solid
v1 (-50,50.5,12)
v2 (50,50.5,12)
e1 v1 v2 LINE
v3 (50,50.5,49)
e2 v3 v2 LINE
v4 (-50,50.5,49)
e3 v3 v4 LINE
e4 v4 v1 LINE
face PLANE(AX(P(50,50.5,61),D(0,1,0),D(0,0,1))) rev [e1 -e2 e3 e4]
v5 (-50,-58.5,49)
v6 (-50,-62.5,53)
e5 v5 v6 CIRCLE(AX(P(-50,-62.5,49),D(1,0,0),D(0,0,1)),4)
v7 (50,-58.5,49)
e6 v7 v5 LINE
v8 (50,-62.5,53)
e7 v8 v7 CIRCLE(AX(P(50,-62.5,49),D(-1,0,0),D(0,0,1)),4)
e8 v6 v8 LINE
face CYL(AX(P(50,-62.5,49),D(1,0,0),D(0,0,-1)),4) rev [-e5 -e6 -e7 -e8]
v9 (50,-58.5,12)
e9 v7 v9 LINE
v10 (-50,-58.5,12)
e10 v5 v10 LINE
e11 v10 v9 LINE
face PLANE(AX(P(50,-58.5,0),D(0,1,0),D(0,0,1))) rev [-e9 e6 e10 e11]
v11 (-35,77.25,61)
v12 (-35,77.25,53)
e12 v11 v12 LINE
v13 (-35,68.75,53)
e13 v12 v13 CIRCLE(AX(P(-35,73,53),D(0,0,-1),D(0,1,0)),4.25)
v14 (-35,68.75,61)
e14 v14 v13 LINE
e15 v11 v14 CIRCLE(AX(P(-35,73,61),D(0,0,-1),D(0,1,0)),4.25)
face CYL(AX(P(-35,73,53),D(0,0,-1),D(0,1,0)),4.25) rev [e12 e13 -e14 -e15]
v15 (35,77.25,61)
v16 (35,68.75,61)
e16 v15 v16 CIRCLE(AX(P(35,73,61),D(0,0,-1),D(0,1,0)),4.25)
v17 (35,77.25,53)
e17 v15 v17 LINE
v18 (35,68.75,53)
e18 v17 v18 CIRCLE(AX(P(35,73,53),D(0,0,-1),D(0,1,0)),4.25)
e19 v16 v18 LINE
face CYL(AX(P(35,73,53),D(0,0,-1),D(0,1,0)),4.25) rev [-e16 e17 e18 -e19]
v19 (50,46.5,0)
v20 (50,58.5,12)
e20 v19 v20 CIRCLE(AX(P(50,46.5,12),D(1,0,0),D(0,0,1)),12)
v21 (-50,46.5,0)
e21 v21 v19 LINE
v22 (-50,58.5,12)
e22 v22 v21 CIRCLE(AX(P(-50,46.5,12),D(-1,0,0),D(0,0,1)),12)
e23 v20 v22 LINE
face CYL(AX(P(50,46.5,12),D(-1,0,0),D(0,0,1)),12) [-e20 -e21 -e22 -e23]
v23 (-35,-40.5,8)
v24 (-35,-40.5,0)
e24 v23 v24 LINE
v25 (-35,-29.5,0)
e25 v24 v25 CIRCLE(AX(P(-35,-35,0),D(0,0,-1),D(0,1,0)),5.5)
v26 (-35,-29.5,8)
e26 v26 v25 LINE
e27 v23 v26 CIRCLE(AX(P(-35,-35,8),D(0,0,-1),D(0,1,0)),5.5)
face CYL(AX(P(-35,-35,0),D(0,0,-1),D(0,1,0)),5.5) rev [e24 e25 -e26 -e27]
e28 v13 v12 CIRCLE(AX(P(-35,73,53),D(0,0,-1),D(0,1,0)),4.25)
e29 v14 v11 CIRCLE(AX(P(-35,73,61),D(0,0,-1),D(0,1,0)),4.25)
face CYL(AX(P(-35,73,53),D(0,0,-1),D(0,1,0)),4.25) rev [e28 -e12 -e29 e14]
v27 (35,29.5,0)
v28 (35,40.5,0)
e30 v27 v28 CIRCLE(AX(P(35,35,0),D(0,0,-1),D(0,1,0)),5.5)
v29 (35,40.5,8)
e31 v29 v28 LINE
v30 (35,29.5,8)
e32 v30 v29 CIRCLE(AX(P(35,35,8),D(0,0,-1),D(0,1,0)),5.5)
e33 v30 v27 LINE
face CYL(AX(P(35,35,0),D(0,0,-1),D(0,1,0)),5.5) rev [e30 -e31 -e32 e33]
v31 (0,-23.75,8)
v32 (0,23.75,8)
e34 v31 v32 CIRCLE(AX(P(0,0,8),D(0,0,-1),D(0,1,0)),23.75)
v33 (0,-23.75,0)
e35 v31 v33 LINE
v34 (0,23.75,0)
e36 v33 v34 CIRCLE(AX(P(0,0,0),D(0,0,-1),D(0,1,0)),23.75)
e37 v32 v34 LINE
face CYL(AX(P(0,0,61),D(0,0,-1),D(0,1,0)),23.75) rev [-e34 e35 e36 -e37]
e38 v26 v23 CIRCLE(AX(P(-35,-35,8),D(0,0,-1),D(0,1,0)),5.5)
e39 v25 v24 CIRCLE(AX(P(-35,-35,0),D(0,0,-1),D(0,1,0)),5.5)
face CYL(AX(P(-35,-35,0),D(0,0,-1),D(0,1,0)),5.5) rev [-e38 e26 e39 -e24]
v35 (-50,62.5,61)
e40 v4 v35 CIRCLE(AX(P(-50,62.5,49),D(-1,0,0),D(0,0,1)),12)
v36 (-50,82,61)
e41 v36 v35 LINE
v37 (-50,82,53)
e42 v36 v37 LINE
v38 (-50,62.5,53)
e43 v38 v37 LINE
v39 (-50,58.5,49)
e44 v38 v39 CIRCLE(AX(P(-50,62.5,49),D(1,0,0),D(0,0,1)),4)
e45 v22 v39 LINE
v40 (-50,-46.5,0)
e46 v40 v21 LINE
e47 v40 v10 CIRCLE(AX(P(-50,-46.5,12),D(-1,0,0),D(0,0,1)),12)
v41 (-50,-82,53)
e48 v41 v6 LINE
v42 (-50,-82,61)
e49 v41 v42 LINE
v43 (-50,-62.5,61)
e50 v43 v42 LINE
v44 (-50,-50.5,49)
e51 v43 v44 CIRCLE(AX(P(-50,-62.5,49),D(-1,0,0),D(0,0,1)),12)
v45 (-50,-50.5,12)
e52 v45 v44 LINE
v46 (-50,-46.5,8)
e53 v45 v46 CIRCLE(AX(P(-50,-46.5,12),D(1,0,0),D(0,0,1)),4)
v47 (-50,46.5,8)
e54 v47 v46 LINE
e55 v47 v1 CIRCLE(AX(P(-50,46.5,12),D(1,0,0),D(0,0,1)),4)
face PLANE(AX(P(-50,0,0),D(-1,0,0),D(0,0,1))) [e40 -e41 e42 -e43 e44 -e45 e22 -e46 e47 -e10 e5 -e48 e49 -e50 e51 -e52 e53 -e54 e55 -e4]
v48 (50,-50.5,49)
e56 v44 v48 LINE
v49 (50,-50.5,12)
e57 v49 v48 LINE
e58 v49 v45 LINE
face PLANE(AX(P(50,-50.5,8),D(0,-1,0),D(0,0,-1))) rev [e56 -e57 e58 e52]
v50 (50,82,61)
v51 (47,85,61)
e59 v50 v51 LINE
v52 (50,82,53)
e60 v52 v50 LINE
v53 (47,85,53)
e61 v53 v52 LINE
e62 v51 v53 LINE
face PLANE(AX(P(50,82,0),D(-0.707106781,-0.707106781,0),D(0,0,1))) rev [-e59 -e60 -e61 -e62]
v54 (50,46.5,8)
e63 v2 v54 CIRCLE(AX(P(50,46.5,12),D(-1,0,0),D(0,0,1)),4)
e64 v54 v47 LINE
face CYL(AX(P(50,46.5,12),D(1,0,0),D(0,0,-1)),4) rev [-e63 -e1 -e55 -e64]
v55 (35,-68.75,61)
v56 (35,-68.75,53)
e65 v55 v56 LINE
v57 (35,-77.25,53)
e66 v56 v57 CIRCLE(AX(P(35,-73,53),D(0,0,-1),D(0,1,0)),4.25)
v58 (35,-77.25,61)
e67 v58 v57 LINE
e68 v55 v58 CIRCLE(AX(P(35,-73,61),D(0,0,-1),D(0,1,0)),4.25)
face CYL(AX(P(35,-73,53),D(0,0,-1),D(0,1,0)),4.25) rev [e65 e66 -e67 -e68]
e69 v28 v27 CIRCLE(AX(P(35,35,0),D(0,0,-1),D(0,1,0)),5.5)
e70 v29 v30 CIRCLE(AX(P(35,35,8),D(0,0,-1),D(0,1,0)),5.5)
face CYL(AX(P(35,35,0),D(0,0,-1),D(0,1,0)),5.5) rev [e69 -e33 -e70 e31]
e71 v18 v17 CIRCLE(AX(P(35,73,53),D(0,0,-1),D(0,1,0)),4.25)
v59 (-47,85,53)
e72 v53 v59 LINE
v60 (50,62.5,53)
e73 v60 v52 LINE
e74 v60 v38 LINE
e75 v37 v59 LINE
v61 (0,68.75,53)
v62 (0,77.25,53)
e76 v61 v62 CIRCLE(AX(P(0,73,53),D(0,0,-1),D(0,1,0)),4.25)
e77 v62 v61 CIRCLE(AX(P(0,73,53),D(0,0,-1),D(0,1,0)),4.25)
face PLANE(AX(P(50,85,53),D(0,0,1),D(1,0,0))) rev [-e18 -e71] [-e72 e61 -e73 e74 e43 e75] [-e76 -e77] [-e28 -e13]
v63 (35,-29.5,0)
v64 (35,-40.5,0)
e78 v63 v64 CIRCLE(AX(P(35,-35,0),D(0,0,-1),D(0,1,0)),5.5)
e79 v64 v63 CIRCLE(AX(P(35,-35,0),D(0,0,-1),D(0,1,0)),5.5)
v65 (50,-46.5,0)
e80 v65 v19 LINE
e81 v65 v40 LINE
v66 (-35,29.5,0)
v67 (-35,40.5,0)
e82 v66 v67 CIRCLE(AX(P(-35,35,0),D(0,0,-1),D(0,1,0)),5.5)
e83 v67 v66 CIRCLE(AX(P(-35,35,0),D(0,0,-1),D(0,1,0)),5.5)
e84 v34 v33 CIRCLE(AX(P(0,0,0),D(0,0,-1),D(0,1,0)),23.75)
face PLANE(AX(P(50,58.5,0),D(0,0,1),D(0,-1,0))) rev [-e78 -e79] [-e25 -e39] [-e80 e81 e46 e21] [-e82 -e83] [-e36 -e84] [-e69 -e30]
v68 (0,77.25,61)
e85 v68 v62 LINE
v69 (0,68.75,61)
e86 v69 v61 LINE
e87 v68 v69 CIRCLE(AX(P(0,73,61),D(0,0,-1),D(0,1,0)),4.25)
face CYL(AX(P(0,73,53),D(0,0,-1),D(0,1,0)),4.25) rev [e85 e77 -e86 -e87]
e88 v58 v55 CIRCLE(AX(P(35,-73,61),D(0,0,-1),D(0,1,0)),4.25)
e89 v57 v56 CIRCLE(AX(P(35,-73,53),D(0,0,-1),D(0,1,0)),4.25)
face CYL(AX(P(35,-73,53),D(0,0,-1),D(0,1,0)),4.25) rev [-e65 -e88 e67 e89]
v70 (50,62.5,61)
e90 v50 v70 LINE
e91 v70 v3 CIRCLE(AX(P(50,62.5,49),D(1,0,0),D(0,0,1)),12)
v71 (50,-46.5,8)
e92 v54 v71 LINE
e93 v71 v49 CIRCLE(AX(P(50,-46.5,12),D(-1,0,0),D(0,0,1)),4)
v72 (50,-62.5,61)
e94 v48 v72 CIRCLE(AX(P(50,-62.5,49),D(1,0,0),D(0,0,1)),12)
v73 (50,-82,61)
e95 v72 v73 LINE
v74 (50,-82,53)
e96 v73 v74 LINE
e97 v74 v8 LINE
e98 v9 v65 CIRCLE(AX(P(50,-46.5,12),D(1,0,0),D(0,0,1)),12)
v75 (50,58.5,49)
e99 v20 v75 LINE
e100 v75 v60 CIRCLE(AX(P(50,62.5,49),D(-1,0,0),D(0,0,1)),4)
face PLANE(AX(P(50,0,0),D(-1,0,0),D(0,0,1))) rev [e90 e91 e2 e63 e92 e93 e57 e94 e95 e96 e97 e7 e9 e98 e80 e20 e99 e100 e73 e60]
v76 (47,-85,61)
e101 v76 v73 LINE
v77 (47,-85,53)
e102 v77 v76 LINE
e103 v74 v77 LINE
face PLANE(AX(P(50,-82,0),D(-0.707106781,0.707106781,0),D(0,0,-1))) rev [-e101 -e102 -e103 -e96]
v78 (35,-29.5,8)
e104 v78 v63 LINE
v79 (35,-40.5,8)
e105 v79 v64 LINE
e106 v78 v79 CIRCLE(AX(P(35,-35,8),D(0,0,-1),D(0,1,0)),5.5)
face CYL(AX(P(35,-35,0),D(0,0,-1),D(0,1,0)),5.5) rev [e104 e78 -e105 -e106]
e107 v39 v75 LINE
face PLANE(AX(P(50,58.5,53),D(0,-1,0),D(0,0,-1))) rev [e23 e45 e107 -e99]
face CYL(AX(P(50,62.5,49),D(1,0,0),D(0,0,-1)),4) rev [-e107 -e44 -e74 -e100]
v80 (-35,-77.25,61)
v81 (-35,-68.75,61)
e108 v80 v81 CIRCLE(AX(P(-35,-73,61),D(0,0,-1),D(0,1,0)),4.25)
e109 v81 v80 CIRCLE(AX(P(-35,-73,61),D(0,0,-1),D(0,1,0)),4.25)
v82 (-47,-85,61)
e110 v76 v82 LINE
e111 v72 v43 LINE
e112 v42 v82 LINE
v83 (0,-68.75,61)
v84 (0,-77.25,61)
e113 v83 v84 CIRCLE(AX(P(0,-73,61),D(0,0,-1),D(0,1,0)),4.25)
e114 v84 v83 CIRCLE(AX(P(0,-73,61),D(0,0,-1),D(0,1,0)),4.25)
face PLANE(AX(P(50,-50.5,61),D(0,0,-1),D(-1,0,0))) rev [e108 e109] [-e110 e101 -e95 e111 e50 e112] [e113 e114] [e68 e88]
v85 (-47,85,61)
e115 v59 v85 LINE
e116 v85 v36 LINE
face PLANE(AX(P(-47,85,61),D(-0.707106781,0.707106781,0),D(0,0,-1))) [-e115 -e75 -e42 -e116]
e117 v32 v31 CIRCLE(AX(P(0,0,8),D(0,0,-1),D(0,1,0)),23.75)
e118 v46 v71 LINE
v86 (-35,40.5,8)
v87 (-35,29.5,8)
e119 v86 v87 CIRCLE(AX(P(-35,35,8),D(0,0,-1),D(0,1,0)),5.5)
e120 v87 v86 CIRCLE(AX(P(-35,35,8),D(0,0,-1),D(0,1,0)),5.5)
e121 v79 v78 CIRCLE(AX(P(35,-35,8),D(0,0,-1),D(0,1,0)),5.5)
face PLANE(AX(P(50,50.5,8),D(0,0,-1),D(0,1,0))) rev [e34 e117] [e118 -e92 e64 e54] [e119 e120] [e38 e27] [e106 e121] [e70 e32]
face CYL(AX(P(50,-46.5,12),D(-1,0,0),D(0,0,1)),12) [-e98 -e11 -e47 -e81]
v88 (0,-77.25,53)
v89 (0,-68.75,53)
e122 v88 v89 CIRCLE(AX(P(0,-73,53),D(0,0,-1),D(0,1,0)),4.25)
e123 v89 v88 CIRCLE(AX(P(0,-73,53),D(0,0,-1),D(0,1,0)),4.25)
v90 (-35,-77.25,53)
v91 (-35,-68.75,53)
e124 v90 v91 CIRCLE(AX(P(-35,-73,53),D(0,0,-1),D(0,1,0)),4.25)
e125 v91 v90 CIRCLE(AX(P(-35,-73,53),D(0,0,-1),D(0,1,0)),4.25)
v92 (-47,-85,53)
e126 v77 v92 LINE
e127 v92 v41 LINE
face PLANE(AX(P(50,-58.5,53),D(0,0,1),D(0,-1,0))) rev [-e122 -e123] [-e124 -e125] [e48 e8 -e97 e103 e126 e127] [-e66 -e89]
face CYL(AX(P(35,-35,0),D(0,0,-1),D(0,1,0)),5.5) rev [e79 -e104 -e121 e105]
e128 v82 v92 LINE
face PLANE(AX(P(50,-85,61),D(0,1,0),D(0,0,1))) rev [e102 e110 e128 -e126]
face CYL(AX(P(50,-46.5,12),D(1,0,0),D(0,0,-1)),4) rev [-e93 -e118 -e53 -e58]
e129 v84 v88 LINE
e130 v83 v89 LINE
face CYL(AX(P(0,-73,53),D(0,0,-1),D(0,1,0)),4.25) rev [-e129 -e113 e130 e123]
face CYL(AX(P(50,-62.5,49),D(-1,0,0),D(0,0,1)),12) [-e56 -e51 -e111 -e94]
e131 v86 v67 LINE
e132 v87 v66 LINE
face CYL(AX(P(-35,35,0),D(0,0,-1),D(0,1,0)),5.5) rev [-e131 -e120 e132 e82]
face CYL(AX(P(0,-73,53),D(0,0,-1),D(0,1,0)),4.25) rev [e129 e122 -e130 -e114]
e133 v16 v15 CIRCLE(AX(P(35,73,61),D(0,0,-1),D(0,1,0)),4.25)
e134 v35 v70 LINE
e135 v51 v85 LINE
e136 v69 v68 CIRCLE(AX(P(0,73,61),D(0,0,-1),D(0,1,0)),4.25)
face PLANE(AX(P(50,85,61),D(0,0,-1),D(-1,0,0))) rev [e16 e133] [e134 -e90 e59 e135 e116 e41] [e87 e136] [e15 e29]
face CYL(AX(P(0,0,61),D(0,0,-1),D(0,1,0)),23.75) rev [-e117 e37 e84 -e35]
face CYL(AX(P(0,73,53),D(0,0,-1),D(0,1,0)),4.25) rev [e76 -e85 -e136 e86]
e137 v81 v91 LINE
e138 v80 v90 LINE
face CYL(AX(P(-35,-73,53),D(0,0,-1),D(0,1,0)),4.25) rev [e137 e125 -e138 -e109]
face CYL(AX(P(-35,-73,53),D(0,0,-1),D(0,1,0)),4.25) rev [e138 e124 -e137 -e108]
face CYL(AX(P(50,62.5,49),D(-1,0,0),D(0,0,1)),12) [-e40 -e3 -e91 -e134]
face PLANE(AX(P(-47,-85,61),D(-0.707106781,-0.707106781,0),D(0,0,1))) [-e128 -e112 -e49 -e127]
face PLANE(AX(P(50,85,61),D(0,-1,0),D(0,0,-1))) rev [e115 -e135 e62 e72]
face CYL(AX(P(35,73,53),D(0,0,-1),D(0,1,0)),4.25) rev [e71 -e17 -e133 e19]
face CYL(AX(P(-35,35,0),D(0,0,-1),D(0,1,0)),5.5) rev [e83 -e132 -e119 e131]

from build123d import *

# Parameters (mm, degrees)
EXTRUDE_1_DEPTH         = 50
SKETCH_3_R              = 23.75
CUT_EXTRUDE_1_DEPTH     = 116.956888541
HOLE_WIZARD_11_0_11_1_D = 11
HOLE_WIZARD_8_5_8_5_1_D = 8.5
CHAMFER_1_SIZE          = 3
FILLET_1_R              = 4
FILLET_2_R              = 12


with BuildPart() as part:
    # 草图1 → 凸台-拉伸1 (new, symmetric)
    with BuildSketch(Plane(origin=(0, 0, 0), x_dir=(0, 0, -1), z_dir=(1, 0, 0))):
        Polygon((-61, 85), (-61, 50.5), (-8, 50.5), (-8, -50.5), (-61, -50.5), (-61, -85), (-53, -85), (-53, -58.5), (0, -58.5), (0, 58.5), (-53, 58.5), (-53, 85), align=None)
    extrude(amount=EXTRUDE_1_DEPTH, both=True)

    # 草图3 → 切除-拉伸1 (cut, through all)
    with BuildSketch(Plane(origin=(0, 0, 0), x_dir=(-1, 0, 0), z_dir=(0, 0, -1))):
        with Locations(Location((0, 0, 0), (0, 0, 90))):
            Circle(SKETCH_3_R)
    extrude(amount=-CUT_EXTRUDE_1_DEPTH, mode=Mode.SUBTRACT)

    # Ø11.0 (11) 直径孔1 (through all)
    with Locations(Plane(origin=(0, 0, 0), x_dir=(-1, 0, 0), z_dir=(0, 0, -1))):
        with Locations((0, 0), (35, -35), (-35, 35), (-35, -35), (35, 35)):
            Hole(HOLE_WIZARD_11_0_11_1_D / 2)

    # Ø8.5 (8.5) 直径孔1 (through all)
    with Locations(Plane(origin=(0, 0, 53), x_dir=(-1, 0, 0), z_dir=(0, 0, -1))):
        with Locations((-35, -73), (0, -73), (35, -73), (35, 73), (0, 73), (-35, 73)):
            Hole(HOLE_WIZARD_8_5_8_5_1_D / 2)

    # 倒角1
    chamfer_1_edges = [part.edges().sort_by_distance(p)[0] for p in [
        (-50, -85, 57),
        (-50, 85, 57),
        (50, -85, 57),
        (50, 85, 57),
    ]]
    chamfer(chamfer_1_edges, length=CHAMFER_1_SIZE)

    # 圆角1
    fillet_1_edges = [part.edges().sort_by_distance(p)[0] for p in [
        (0, 58.5, 53),
        (0, -58.5, 53),
        (0, -50.5, 8),
        (0, 50.5, 8),
    ]]
    fillet(fillet_1_edges, radius=FILLET_1_R)

    # 圆角2
    fillet_2_edges = [part.edges().sort_by_distance(p)[0] for p in [
        (0, 58.5, 0),
        (0, -58.5, 0),
        (0, -50.5, 61),
        (0, 50.5, 61),
    ]]
    fillet(fillet_2_edges, radius=FILLET_2_R)


solid = part.part
